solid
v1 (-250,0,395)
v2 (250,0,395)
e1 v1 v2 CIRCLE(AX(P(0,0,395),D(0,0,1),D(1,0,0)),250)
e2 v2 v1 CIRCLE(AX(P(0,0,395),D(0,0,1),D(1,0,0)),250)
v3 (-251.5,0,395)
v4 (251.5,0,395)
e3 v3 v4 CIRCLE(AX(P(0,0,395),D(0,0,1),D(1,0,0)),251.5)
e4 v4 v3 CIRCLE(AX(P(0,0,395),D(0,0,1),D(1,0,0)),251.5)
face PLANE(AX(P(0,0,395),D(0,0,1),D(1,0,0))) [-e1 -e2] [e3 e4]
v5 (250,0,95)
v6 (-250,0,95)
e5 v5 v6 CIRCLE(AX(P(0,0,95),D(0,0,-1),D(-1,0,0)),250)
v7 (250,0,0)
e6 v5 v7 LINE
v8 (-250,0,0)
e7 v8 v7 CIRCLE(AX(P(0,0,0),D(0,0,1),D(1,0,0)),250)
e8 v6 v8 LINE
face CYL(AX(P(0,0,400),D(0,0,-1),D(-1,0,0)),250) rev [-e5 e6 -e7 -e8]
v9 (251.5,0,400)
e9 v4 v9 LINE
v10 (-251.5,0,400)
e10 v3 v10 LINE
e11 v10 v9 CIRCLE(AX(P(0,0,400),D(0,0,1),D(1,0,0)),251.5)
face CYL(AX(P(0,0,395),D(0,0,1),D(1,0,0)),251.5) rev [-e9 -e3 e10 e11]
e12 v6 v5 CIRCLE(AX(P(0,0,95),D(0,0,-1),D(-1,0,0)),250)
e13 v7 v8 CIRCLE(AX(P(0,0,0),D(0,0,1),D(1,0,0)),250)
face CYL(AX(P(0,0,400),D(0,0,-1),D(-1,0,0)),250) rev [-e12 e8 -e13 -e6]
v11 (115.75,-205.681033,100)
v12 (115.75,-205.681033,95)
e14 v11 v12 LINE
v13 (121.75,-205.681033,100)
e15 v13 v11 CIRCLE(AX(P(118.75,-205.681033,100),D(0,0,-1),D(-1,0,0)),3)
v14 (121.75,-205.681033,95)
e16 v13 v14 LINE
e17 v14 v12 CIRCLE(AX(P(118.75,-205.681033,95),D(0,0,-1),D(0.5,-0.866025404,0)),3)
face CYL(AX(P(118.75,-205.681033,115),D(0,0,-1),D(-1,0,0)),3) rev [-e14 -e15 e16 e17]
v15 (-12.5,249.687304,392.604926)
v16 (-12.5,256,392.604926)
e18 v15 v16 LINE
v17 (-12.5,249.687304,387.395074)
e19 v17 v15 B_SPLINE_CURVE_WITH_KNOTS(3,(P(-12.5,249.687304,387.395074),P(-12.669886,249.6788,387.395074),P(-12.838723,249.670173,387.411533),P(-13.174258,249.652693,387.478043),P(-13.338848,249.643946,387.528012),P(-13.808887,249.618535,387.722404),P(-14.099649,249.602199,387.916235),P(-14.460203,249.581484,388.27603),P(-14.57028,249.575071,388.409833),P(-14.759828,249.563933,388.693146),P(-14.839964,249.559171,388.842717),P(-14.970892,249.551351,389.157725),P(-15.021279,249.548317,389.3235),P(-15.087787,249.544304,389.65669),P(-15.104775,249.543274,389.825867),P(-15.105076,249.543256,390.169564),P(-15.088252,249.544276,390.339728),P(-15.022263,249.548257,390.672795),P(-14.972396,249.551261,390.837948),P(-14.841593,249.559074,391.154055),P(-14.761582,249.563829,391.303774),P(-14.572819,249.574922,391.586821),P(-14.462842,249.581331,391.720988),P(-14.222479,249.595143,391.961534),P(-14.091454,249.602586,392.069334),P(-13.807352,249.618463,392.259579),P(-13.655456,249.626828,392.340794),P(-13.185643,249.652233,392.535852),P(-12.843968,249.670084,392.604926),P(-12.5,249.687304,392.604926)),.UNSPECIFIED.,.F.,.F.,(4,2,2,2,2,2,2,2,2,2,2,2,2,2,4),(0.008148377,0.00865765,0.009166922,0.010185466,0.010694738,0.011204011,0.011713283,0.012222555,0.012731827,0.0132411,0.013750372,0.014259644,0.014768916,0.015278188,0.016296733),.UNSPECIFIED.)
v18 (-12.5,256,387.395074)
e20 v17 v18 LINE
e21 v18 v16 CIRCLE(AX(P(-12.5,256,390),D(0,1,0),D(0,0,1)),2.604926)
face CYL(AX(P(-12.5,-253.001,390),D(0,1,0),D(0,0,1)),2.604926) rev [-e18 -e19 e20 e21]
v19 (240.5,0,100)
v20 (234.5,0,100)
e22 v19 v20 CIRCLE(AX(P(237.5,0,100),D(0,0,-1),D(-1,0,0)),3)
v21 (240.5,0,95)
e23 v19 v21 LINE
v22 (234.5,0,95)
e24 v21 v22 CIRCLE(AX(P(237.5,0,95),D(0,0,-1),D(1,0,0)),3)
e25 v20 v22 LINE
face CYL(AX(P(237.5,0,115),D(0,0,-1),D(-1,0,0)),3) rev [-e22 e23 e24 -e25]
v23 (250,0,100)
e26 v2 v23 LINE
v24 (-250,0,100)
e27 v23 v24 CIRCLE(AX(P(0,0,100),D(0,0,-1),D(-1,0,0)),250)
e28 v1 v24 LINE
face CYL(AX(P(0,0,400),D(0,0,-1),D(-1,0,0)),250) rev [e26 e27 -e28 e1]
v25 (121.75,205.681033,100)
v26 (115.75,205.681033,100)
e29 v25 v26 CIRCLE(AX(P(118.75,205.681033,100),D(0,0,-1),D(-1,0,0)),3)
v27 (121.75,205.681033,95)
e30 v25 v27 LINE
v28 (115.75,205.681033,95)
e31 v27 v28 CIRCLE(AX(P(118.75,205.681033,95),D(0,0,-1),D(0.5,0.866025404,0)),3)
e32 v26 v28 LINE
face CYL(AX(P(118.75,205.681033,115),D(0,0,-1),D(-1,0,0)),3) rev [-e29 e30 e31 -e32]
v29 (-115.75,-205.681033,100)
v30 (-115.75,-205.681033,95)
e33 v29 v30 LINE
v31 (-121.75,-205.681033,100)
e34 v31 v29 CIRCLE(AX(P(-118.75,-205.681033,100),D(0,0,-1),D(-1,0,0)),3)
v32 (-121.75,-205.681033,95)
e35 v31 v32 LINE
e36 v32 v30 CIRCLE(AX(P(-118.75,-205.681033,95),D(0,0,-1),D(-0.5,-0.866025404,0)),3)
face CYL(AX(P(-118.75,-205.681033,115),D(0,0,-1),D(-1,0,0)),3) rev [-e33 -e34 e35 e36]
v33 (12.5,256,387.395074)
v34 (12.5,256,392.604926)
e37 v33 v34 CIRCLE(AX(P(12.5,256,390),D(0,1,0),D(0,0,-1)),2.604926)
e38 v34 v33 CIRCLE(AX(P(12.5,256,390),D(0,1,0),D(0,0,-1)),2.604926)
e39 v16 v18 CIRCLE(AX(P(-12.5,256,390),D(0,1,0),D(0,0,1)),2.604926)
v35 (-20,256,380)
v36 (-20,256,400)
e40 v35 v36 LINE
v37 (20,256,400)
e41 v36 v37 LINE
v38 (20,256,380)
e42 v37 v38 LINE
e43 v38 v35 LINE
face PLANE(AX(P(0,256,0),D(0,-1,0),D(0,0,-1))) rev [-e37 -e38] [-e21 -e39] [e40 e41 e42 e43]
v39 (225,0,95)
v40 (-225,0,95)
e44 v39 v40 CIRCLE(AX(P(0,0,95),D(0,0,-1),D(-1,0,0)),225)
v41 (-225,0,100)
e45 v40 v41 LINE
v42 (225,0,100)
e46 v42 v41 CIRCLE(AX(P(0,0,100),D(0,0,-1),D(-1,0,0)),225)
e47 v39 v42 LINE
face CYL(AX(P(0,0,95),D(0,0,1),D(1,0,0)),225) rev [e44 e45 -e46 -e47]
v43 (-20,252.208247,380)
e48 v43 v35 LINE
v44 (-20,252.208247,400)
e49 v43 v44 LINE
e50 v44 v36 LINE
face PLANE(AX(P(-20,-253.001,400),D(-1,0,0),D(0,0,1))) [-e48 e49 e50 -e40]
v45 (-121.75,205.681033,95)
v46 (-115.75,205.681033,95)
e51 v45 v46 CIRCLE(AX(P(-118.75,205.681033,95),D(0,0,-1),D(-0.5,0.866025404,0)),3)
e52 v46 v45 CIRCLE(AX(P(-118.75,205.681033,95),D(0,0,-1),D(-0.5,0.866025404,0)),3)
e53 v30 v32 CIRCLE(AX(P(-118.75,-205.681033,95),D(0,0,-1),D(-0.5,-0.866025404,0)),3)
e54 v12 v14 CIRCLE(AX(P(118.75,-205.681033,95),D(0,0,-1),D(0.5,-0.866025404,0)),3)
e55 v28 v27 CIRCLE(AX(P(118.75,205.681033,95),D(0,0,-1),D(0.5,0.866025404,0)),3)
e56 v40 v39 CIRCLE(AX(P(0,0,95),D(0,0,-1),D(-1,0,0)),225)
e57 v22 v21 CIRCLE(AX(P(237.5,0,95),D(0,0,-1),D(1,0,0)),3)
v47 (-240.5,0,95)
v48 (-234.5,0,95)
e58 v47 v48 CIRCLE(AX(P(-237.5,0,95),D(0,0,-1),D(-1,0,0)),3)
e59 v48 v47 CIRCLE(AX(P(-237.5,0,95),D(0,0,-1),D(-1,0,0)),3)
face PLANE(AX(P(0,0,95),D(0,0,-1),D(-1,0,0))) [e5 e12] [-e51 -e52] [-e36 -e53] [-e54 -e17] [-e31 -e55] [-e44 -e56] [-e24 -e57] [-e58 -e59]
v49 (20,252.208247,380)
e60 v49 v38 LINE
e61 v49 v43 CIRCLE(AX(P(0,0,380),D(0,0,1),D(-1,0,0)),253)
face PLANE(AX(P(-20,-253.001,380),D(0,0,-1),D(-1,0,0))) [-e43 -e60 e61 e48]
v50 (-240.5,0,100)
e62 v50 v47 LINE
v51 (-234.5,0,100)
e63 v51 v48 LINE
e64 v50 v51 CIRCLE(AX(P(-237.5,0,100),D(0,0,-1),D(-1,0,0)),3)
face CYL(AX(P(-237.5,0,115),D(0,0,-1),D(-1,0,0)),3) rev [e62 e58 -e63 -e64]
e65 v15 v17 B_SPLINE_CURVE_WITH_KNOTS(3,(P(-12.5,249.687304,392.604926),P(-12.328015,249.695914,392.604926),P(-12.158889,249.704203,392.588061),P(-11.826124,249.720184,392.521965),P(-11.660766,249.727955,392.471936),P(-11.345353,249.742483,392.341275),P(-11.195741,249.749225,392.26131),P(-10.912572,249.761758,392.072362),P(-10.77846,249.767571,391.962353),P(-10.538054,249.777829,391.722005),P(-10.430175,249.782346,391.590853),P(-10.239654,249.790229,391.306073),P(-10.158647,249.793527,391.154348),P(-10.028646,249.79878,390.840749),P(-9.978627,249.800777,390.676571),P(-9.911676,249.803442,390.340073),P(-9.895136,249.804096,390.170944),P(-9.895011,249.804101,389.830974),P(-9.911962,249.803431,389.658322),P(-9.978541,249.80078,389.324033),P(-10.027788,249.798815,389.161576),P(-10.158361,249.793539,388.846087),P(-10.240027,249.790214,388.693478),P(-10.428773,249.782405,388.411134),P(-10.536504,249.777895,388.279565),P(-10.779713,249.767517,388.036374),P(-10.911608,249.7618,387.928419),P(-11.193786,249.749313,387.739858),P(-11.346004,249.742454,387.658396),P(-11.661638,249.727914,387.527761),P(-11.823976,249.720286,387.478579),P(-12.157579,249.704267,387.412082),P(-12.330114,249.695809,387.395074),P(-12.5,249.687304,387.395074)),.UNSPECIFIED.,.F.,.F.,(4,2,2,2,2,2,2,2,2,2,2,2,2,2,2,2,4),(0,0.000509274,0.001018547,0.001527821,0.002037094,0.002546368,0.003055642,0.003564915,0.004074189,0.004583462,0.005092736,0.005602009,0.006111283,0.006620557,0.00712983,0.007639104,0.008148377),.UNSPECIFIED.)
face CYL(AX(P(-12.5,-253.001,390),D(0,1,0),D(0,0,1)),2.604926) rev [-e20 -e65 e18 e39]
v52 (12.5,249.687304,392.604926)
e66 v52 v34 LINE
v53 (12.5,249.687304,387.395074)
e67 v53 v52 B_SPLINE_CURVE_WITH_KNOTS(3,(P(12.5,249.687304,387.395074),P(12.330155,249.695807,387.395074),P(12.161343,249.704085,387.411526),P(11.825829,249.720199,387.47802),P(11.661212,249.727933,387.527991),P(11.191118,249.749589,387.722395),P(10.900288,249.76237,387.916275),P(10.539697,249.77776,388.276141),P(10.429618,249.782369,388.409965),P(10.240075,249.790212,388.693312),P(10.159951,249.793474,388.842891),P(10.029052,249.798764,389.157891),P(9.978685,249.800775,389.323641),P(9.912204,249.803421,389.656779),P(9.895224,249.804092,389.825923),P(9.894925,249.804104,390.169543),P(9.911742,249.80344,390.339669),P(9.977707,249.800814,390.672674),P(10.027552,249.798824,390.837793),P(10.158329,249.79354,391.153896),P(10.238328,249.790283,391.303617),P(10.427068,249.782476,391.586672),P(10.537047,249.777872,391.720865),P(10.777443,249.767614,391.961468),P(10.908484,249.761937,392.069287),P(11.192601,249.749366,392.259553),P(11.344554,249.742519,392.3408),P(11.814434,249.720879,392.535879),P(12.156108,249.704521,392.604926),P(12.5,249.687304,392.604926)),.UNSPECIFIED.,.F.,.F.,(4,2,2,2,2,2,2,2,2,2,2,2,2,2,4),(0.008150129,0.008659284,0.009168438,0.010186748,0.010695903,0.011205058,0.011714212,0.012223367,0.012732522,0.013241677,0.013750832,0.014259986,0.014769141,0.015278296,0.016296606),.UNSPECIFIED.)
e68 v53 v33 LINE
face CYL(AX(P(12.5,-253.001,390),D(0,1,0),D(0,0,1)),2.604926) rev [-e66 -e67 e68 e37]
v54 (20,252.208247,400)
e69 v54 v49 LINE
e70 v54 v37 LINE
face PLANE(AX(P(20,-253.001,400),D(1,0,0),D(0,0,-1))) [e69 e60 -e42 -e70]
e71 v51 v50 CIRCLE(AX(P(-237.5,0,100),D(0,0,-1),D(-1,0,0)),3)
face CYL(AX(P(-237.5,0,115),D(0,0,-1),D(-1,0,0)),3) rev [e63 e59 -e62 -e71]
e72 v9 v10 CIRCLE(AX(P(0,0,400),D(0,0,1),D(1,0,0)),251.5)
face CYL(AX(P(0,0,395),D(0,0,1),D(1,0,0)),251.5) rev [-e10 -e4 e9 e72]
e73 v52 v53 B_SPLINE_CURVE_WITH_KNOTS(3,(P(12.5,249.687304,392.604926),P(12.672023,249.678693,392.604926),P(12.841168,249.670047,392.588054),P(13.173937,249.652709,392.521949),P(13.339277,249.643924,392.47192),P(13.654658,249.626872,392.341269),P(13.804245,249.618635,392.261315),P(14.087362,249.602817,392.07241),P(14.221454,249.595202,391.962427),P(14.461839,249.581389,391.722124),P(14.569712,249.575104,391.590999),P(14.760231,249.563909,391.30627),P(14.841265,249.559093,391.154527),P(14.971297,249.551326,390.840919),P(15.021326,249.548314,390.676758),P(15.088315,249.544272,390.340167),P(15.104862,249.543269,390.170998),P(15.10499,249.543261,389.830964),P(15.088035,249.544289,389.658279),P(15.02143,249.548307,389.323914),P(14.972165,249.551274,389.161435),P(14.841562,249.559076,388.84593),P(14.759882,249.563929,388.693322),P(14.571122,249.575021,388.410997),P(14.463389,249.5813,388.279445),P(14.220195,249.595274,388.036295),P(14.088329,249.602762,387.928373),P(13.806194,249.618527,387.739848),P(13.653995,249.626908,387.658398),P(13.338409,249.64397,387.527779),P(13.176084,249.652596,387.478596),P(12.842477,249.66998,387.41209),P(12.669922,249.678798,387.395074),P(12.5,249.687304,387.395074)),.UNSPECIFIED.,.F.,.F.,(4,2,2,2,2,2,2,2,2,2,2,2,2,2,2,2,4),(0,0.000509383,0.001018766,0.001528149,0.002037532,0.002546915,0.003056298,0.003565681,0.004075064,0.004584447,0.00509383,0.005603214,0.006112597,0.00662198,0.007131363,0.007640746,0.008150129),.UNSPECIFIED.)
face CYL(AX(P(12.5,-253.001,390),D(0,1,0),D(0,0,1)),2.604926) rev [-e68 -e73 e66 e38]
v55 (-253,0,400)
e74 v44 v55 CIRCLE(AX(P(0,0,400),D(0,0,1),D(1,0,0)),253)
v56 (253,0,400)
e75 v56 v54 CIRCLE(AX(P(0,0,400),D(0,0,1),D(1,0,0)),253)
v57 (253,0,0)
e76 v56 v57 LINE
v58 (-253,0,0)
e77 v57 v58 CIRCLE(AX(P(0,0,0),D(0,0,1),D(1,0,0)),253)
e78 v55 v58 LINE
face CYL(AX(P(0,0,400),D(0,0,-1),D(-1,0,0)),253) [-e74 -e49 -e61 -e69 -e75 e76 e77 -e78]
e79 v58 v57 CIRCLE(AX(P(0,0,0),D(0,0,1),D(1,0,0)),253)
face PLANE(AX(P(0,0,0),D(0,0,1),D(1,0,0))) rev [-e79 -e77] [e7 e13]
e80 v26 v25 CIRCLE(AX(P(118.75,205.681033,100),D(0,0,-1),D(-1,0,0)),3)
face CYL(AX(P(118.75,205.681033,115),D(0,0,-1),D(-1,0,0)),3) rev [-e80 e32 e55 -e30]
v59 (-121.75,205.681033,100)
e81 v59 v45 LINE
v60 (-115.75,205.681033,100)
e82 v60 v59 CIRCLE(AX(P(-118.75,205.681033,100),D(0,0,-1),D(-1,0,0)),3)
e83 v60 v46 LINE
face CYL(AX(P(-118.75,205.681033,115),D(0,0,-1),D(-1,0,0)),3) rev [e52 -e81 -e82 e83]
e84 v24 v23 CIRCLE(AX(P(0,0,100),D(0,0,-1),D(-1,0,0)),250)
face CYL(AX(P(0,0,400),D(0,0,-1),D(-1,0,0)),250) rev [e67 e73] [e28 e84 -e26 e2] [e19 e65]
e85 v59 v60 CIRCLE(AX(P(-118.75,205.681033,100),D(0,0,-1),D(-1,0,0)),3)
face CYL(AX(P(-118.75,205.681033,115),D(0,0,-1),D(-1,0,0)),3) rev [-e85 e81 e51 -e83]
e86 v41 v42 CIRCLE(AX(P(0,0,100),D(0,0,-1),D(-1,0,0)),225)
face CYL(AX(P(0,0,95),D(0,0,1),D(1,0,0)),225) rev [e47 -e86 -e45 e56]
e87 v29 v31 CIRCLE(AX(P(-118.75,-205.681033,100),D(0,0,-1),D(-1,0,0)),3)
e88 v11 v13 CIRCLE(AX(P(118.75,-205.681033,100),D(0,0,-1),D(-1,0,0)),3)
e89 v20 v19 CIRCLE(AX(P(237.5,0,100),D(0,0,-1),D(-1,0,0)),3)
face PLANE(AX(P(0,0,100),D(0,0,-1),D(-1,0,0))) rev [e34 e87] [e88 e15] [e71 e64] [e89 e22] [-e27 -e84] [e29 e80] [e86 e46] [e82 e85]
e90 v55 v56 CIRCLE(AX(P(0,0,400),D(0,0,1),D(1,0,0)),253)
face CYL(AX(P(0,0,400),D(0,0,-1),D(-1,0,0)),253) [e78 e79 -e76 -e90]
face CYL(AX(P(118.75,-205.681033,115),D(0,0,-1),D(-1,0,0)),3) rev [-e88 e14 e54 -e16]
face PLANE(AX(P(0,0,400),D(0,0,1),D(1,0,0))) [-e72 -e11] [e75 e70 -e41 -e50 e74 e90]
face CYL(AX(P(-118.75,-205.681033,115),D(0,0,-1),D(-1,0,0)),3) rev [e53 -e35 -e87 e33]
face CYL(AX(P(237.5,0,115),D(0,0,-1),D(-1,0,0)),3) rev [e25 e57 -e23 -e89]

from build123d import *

# Parameters (mm, degrees)
SKETCH1_R                = 253
SKETCH1_R_2              = 250
BOSS_EXTRUDE1_DEPTH      = 400
BOSS_EXTRUDE2_START      = -95
SKETCH2_R                = 250
SKETCH2_R_2              = 225
BOSS_EXTRUDE2_DEPTH      = 5
SKETCH3_R                = 3
CUT_EXTRUDE1_DEPTH       = 20
CIRPATTERN1_COUNT        = 6
BOSS_EXTRUDE4_REACH      = 697.047
BOSS_EXTRUDE4_END_RADIUS = 253
SKETCH6_W                = 40
SKETCH6_H                = 20
CUT_EXTRUDE2_REACH       = 697.047
CUT_EXTRUDE2_END_RADIUS  = 250
SKETCH8_R                = 2.604926317
CUT_EXTRUDE3_START       = -5
SKETCH9_R                = 251.5
SKETCH9_R_2              = 250
CUT_EXTRUDE3_DEPTH       = 5


with BuildPart() as part:
    # Sketch1 → Boss-Extrude1 (new body)
    with BuildSketch(Plane.XY):
        Circle(SKETCH1_R)
        Circle(SKETCH1_R_2, mode=Mode.SUBTRACT)
    extrude(amount=BOSS_EXTRUDE1_DEPTH)

    # Sketch2 → Boss-Extrude2 (add)
    with BuildSketch(Plane(origin=(0, 0, 0), x_dir=(-1, 0, 0), z_dir=(0, 0, -1)).offset(BOSS_EXTRUDE2_START)):
        Circle(SKETCH2_R)
        Circle(SKETCH2_R_2, mode=Mode.SUBTRACT)
    extrude(amount=-BOSS_EXTRUDE2_DEPTH)

    # Sketch3 → Cut-Extrude1 (cut)
    with BuildSketch(Plane(origin=(0, 0, 95), x_dir=(-1, 0, 0), z_dir=(0, 0, -1))):
        with Locations((237.5, 0)):
            Circle(SKETCH3_R)
    cut_extrude1 = extrude(amount=-CUT_EXTRUDE1_DEPTH, mode=Mode.SUBTRACT)

    # CirPattern1: Cut-Extrude1 ×6 about axis
    cirpattern1_axis = Axis((0, 0, 0), (0, 0, 1))
    for i in range(1, CIRPATTERN1_COUNT):
        add(cut_extrude1.rotate(cirpattern1_axis, i * 360 / CIRPATTERN1_COUNT), mode=Mode.SUBTRACT)

    # Boss-Extrude4: up to this cylinder (the profile starts outside it)
    boss_extrude4_end = Plane(origin=(0, 0, 390), z_dir=(0, 0, -1)) * Cylinder(BOSS_EXTRUDE4_END_RADIUS, 1901.094, mode=Mode.PRIVATE)
    # Sketch6 → Boss-Extrude4 (add, up to the surface)
    with BuildSketch(Plane(origin=(0, 256, 0), x_dir=(1, 0, 0), z_dir=(0, 1, 0)), mode=Mode.PRIVATE) as boss_extrude4_sk1:
        with Locations((0, -390)):
            Rectangle(SKETCH6_W, SKETCH6_H)
    boss_extrude4_tool1 = extrude(boss_extrude4_sk1.sketch, amount=-BOSS_EXTRUDE4_REACH, mode=Mode.PRIVATE) - boss_extrude4_end
    add(boss_extrude4_tool1.solids().sort_by_distance((0, 256, 390))[0])

    # Cut-Extrude2: up to this cylinder (the profile starts outside it)
    cut_extrude2_end = Plane(origin=(0, 0, 390), z_dir=(0, 0, -1)) * Cylinder(CUT_EXTRUDE2_END_RADIUS, 1895.094, mode=Mode.PRIVATE)
    # Sketch8 → Cut-Extrude2 (cut, up to the surface)
    with BuildSketch(Plane(origin=(0, 256, 0), x_dir=(1, 0, 0), z_dir=(0, 1, 0)), mode=Mode.PRIVATE) as cut_extrude2_sk1:
        with Locations(Location((-12.5, -390, 0), (0, 0, 270))):
            Circle(SKETCH8_R)
    cut_extrude2_tool1 = extrude(cut_extrude2_sk1.sketch, amount=-CUT_EXTRUDE2_REACH, mode=Mode.PRIVATE) - cut_extrude2_end
    add(cut_extrude2_tool1.solids().sort_by_distance((-12.5, 256, 390))[0], mode=Mode.SUBTRACT)
    # Sketch8 → Cut-Extrude2 (cut, up to the surface)
    with BuildSketch(Plane(origin=(0, 256, 0), x_dir=(1, 0, 0), z_dir=(0, 1, 0)), mode=Mode.PRIVATE) as cut_extrude2_sk2:
        with Locations(Location((12.5, -390, 0), (0, 0, 270))):
            Circle(SKETCH8_R)
    cut_extrude2_tool2 = extrude(cut_extrude2_sk2.sketch, amount=-CUT_EXTRUDE2_REACH, mode=Mode.PRIVATE) - cut_extrude2_end
    add(cut_extrude2_tool2.solids().sort_by_distance((12.5, 256, 390))[0], mode=Mode.SUBTRACT)

    # Sketch9 → Cut-Extrude3 (cut)
    with BuildSketch(Plane.XY.offset(400).offset(CUT_EXTRUDE3_START)):
        Circle(SKETCH9_R)
        with Locations(Location((0, 0, 0), (0, 0, 180))):
            Circle(SKETCH9_R_2, mode=Mode.SUBTRACT)
    extrude(amount=CUT_EXTRUDE3_DEPTH, mode=Mode.SUBTRACT)


solid = part.part
